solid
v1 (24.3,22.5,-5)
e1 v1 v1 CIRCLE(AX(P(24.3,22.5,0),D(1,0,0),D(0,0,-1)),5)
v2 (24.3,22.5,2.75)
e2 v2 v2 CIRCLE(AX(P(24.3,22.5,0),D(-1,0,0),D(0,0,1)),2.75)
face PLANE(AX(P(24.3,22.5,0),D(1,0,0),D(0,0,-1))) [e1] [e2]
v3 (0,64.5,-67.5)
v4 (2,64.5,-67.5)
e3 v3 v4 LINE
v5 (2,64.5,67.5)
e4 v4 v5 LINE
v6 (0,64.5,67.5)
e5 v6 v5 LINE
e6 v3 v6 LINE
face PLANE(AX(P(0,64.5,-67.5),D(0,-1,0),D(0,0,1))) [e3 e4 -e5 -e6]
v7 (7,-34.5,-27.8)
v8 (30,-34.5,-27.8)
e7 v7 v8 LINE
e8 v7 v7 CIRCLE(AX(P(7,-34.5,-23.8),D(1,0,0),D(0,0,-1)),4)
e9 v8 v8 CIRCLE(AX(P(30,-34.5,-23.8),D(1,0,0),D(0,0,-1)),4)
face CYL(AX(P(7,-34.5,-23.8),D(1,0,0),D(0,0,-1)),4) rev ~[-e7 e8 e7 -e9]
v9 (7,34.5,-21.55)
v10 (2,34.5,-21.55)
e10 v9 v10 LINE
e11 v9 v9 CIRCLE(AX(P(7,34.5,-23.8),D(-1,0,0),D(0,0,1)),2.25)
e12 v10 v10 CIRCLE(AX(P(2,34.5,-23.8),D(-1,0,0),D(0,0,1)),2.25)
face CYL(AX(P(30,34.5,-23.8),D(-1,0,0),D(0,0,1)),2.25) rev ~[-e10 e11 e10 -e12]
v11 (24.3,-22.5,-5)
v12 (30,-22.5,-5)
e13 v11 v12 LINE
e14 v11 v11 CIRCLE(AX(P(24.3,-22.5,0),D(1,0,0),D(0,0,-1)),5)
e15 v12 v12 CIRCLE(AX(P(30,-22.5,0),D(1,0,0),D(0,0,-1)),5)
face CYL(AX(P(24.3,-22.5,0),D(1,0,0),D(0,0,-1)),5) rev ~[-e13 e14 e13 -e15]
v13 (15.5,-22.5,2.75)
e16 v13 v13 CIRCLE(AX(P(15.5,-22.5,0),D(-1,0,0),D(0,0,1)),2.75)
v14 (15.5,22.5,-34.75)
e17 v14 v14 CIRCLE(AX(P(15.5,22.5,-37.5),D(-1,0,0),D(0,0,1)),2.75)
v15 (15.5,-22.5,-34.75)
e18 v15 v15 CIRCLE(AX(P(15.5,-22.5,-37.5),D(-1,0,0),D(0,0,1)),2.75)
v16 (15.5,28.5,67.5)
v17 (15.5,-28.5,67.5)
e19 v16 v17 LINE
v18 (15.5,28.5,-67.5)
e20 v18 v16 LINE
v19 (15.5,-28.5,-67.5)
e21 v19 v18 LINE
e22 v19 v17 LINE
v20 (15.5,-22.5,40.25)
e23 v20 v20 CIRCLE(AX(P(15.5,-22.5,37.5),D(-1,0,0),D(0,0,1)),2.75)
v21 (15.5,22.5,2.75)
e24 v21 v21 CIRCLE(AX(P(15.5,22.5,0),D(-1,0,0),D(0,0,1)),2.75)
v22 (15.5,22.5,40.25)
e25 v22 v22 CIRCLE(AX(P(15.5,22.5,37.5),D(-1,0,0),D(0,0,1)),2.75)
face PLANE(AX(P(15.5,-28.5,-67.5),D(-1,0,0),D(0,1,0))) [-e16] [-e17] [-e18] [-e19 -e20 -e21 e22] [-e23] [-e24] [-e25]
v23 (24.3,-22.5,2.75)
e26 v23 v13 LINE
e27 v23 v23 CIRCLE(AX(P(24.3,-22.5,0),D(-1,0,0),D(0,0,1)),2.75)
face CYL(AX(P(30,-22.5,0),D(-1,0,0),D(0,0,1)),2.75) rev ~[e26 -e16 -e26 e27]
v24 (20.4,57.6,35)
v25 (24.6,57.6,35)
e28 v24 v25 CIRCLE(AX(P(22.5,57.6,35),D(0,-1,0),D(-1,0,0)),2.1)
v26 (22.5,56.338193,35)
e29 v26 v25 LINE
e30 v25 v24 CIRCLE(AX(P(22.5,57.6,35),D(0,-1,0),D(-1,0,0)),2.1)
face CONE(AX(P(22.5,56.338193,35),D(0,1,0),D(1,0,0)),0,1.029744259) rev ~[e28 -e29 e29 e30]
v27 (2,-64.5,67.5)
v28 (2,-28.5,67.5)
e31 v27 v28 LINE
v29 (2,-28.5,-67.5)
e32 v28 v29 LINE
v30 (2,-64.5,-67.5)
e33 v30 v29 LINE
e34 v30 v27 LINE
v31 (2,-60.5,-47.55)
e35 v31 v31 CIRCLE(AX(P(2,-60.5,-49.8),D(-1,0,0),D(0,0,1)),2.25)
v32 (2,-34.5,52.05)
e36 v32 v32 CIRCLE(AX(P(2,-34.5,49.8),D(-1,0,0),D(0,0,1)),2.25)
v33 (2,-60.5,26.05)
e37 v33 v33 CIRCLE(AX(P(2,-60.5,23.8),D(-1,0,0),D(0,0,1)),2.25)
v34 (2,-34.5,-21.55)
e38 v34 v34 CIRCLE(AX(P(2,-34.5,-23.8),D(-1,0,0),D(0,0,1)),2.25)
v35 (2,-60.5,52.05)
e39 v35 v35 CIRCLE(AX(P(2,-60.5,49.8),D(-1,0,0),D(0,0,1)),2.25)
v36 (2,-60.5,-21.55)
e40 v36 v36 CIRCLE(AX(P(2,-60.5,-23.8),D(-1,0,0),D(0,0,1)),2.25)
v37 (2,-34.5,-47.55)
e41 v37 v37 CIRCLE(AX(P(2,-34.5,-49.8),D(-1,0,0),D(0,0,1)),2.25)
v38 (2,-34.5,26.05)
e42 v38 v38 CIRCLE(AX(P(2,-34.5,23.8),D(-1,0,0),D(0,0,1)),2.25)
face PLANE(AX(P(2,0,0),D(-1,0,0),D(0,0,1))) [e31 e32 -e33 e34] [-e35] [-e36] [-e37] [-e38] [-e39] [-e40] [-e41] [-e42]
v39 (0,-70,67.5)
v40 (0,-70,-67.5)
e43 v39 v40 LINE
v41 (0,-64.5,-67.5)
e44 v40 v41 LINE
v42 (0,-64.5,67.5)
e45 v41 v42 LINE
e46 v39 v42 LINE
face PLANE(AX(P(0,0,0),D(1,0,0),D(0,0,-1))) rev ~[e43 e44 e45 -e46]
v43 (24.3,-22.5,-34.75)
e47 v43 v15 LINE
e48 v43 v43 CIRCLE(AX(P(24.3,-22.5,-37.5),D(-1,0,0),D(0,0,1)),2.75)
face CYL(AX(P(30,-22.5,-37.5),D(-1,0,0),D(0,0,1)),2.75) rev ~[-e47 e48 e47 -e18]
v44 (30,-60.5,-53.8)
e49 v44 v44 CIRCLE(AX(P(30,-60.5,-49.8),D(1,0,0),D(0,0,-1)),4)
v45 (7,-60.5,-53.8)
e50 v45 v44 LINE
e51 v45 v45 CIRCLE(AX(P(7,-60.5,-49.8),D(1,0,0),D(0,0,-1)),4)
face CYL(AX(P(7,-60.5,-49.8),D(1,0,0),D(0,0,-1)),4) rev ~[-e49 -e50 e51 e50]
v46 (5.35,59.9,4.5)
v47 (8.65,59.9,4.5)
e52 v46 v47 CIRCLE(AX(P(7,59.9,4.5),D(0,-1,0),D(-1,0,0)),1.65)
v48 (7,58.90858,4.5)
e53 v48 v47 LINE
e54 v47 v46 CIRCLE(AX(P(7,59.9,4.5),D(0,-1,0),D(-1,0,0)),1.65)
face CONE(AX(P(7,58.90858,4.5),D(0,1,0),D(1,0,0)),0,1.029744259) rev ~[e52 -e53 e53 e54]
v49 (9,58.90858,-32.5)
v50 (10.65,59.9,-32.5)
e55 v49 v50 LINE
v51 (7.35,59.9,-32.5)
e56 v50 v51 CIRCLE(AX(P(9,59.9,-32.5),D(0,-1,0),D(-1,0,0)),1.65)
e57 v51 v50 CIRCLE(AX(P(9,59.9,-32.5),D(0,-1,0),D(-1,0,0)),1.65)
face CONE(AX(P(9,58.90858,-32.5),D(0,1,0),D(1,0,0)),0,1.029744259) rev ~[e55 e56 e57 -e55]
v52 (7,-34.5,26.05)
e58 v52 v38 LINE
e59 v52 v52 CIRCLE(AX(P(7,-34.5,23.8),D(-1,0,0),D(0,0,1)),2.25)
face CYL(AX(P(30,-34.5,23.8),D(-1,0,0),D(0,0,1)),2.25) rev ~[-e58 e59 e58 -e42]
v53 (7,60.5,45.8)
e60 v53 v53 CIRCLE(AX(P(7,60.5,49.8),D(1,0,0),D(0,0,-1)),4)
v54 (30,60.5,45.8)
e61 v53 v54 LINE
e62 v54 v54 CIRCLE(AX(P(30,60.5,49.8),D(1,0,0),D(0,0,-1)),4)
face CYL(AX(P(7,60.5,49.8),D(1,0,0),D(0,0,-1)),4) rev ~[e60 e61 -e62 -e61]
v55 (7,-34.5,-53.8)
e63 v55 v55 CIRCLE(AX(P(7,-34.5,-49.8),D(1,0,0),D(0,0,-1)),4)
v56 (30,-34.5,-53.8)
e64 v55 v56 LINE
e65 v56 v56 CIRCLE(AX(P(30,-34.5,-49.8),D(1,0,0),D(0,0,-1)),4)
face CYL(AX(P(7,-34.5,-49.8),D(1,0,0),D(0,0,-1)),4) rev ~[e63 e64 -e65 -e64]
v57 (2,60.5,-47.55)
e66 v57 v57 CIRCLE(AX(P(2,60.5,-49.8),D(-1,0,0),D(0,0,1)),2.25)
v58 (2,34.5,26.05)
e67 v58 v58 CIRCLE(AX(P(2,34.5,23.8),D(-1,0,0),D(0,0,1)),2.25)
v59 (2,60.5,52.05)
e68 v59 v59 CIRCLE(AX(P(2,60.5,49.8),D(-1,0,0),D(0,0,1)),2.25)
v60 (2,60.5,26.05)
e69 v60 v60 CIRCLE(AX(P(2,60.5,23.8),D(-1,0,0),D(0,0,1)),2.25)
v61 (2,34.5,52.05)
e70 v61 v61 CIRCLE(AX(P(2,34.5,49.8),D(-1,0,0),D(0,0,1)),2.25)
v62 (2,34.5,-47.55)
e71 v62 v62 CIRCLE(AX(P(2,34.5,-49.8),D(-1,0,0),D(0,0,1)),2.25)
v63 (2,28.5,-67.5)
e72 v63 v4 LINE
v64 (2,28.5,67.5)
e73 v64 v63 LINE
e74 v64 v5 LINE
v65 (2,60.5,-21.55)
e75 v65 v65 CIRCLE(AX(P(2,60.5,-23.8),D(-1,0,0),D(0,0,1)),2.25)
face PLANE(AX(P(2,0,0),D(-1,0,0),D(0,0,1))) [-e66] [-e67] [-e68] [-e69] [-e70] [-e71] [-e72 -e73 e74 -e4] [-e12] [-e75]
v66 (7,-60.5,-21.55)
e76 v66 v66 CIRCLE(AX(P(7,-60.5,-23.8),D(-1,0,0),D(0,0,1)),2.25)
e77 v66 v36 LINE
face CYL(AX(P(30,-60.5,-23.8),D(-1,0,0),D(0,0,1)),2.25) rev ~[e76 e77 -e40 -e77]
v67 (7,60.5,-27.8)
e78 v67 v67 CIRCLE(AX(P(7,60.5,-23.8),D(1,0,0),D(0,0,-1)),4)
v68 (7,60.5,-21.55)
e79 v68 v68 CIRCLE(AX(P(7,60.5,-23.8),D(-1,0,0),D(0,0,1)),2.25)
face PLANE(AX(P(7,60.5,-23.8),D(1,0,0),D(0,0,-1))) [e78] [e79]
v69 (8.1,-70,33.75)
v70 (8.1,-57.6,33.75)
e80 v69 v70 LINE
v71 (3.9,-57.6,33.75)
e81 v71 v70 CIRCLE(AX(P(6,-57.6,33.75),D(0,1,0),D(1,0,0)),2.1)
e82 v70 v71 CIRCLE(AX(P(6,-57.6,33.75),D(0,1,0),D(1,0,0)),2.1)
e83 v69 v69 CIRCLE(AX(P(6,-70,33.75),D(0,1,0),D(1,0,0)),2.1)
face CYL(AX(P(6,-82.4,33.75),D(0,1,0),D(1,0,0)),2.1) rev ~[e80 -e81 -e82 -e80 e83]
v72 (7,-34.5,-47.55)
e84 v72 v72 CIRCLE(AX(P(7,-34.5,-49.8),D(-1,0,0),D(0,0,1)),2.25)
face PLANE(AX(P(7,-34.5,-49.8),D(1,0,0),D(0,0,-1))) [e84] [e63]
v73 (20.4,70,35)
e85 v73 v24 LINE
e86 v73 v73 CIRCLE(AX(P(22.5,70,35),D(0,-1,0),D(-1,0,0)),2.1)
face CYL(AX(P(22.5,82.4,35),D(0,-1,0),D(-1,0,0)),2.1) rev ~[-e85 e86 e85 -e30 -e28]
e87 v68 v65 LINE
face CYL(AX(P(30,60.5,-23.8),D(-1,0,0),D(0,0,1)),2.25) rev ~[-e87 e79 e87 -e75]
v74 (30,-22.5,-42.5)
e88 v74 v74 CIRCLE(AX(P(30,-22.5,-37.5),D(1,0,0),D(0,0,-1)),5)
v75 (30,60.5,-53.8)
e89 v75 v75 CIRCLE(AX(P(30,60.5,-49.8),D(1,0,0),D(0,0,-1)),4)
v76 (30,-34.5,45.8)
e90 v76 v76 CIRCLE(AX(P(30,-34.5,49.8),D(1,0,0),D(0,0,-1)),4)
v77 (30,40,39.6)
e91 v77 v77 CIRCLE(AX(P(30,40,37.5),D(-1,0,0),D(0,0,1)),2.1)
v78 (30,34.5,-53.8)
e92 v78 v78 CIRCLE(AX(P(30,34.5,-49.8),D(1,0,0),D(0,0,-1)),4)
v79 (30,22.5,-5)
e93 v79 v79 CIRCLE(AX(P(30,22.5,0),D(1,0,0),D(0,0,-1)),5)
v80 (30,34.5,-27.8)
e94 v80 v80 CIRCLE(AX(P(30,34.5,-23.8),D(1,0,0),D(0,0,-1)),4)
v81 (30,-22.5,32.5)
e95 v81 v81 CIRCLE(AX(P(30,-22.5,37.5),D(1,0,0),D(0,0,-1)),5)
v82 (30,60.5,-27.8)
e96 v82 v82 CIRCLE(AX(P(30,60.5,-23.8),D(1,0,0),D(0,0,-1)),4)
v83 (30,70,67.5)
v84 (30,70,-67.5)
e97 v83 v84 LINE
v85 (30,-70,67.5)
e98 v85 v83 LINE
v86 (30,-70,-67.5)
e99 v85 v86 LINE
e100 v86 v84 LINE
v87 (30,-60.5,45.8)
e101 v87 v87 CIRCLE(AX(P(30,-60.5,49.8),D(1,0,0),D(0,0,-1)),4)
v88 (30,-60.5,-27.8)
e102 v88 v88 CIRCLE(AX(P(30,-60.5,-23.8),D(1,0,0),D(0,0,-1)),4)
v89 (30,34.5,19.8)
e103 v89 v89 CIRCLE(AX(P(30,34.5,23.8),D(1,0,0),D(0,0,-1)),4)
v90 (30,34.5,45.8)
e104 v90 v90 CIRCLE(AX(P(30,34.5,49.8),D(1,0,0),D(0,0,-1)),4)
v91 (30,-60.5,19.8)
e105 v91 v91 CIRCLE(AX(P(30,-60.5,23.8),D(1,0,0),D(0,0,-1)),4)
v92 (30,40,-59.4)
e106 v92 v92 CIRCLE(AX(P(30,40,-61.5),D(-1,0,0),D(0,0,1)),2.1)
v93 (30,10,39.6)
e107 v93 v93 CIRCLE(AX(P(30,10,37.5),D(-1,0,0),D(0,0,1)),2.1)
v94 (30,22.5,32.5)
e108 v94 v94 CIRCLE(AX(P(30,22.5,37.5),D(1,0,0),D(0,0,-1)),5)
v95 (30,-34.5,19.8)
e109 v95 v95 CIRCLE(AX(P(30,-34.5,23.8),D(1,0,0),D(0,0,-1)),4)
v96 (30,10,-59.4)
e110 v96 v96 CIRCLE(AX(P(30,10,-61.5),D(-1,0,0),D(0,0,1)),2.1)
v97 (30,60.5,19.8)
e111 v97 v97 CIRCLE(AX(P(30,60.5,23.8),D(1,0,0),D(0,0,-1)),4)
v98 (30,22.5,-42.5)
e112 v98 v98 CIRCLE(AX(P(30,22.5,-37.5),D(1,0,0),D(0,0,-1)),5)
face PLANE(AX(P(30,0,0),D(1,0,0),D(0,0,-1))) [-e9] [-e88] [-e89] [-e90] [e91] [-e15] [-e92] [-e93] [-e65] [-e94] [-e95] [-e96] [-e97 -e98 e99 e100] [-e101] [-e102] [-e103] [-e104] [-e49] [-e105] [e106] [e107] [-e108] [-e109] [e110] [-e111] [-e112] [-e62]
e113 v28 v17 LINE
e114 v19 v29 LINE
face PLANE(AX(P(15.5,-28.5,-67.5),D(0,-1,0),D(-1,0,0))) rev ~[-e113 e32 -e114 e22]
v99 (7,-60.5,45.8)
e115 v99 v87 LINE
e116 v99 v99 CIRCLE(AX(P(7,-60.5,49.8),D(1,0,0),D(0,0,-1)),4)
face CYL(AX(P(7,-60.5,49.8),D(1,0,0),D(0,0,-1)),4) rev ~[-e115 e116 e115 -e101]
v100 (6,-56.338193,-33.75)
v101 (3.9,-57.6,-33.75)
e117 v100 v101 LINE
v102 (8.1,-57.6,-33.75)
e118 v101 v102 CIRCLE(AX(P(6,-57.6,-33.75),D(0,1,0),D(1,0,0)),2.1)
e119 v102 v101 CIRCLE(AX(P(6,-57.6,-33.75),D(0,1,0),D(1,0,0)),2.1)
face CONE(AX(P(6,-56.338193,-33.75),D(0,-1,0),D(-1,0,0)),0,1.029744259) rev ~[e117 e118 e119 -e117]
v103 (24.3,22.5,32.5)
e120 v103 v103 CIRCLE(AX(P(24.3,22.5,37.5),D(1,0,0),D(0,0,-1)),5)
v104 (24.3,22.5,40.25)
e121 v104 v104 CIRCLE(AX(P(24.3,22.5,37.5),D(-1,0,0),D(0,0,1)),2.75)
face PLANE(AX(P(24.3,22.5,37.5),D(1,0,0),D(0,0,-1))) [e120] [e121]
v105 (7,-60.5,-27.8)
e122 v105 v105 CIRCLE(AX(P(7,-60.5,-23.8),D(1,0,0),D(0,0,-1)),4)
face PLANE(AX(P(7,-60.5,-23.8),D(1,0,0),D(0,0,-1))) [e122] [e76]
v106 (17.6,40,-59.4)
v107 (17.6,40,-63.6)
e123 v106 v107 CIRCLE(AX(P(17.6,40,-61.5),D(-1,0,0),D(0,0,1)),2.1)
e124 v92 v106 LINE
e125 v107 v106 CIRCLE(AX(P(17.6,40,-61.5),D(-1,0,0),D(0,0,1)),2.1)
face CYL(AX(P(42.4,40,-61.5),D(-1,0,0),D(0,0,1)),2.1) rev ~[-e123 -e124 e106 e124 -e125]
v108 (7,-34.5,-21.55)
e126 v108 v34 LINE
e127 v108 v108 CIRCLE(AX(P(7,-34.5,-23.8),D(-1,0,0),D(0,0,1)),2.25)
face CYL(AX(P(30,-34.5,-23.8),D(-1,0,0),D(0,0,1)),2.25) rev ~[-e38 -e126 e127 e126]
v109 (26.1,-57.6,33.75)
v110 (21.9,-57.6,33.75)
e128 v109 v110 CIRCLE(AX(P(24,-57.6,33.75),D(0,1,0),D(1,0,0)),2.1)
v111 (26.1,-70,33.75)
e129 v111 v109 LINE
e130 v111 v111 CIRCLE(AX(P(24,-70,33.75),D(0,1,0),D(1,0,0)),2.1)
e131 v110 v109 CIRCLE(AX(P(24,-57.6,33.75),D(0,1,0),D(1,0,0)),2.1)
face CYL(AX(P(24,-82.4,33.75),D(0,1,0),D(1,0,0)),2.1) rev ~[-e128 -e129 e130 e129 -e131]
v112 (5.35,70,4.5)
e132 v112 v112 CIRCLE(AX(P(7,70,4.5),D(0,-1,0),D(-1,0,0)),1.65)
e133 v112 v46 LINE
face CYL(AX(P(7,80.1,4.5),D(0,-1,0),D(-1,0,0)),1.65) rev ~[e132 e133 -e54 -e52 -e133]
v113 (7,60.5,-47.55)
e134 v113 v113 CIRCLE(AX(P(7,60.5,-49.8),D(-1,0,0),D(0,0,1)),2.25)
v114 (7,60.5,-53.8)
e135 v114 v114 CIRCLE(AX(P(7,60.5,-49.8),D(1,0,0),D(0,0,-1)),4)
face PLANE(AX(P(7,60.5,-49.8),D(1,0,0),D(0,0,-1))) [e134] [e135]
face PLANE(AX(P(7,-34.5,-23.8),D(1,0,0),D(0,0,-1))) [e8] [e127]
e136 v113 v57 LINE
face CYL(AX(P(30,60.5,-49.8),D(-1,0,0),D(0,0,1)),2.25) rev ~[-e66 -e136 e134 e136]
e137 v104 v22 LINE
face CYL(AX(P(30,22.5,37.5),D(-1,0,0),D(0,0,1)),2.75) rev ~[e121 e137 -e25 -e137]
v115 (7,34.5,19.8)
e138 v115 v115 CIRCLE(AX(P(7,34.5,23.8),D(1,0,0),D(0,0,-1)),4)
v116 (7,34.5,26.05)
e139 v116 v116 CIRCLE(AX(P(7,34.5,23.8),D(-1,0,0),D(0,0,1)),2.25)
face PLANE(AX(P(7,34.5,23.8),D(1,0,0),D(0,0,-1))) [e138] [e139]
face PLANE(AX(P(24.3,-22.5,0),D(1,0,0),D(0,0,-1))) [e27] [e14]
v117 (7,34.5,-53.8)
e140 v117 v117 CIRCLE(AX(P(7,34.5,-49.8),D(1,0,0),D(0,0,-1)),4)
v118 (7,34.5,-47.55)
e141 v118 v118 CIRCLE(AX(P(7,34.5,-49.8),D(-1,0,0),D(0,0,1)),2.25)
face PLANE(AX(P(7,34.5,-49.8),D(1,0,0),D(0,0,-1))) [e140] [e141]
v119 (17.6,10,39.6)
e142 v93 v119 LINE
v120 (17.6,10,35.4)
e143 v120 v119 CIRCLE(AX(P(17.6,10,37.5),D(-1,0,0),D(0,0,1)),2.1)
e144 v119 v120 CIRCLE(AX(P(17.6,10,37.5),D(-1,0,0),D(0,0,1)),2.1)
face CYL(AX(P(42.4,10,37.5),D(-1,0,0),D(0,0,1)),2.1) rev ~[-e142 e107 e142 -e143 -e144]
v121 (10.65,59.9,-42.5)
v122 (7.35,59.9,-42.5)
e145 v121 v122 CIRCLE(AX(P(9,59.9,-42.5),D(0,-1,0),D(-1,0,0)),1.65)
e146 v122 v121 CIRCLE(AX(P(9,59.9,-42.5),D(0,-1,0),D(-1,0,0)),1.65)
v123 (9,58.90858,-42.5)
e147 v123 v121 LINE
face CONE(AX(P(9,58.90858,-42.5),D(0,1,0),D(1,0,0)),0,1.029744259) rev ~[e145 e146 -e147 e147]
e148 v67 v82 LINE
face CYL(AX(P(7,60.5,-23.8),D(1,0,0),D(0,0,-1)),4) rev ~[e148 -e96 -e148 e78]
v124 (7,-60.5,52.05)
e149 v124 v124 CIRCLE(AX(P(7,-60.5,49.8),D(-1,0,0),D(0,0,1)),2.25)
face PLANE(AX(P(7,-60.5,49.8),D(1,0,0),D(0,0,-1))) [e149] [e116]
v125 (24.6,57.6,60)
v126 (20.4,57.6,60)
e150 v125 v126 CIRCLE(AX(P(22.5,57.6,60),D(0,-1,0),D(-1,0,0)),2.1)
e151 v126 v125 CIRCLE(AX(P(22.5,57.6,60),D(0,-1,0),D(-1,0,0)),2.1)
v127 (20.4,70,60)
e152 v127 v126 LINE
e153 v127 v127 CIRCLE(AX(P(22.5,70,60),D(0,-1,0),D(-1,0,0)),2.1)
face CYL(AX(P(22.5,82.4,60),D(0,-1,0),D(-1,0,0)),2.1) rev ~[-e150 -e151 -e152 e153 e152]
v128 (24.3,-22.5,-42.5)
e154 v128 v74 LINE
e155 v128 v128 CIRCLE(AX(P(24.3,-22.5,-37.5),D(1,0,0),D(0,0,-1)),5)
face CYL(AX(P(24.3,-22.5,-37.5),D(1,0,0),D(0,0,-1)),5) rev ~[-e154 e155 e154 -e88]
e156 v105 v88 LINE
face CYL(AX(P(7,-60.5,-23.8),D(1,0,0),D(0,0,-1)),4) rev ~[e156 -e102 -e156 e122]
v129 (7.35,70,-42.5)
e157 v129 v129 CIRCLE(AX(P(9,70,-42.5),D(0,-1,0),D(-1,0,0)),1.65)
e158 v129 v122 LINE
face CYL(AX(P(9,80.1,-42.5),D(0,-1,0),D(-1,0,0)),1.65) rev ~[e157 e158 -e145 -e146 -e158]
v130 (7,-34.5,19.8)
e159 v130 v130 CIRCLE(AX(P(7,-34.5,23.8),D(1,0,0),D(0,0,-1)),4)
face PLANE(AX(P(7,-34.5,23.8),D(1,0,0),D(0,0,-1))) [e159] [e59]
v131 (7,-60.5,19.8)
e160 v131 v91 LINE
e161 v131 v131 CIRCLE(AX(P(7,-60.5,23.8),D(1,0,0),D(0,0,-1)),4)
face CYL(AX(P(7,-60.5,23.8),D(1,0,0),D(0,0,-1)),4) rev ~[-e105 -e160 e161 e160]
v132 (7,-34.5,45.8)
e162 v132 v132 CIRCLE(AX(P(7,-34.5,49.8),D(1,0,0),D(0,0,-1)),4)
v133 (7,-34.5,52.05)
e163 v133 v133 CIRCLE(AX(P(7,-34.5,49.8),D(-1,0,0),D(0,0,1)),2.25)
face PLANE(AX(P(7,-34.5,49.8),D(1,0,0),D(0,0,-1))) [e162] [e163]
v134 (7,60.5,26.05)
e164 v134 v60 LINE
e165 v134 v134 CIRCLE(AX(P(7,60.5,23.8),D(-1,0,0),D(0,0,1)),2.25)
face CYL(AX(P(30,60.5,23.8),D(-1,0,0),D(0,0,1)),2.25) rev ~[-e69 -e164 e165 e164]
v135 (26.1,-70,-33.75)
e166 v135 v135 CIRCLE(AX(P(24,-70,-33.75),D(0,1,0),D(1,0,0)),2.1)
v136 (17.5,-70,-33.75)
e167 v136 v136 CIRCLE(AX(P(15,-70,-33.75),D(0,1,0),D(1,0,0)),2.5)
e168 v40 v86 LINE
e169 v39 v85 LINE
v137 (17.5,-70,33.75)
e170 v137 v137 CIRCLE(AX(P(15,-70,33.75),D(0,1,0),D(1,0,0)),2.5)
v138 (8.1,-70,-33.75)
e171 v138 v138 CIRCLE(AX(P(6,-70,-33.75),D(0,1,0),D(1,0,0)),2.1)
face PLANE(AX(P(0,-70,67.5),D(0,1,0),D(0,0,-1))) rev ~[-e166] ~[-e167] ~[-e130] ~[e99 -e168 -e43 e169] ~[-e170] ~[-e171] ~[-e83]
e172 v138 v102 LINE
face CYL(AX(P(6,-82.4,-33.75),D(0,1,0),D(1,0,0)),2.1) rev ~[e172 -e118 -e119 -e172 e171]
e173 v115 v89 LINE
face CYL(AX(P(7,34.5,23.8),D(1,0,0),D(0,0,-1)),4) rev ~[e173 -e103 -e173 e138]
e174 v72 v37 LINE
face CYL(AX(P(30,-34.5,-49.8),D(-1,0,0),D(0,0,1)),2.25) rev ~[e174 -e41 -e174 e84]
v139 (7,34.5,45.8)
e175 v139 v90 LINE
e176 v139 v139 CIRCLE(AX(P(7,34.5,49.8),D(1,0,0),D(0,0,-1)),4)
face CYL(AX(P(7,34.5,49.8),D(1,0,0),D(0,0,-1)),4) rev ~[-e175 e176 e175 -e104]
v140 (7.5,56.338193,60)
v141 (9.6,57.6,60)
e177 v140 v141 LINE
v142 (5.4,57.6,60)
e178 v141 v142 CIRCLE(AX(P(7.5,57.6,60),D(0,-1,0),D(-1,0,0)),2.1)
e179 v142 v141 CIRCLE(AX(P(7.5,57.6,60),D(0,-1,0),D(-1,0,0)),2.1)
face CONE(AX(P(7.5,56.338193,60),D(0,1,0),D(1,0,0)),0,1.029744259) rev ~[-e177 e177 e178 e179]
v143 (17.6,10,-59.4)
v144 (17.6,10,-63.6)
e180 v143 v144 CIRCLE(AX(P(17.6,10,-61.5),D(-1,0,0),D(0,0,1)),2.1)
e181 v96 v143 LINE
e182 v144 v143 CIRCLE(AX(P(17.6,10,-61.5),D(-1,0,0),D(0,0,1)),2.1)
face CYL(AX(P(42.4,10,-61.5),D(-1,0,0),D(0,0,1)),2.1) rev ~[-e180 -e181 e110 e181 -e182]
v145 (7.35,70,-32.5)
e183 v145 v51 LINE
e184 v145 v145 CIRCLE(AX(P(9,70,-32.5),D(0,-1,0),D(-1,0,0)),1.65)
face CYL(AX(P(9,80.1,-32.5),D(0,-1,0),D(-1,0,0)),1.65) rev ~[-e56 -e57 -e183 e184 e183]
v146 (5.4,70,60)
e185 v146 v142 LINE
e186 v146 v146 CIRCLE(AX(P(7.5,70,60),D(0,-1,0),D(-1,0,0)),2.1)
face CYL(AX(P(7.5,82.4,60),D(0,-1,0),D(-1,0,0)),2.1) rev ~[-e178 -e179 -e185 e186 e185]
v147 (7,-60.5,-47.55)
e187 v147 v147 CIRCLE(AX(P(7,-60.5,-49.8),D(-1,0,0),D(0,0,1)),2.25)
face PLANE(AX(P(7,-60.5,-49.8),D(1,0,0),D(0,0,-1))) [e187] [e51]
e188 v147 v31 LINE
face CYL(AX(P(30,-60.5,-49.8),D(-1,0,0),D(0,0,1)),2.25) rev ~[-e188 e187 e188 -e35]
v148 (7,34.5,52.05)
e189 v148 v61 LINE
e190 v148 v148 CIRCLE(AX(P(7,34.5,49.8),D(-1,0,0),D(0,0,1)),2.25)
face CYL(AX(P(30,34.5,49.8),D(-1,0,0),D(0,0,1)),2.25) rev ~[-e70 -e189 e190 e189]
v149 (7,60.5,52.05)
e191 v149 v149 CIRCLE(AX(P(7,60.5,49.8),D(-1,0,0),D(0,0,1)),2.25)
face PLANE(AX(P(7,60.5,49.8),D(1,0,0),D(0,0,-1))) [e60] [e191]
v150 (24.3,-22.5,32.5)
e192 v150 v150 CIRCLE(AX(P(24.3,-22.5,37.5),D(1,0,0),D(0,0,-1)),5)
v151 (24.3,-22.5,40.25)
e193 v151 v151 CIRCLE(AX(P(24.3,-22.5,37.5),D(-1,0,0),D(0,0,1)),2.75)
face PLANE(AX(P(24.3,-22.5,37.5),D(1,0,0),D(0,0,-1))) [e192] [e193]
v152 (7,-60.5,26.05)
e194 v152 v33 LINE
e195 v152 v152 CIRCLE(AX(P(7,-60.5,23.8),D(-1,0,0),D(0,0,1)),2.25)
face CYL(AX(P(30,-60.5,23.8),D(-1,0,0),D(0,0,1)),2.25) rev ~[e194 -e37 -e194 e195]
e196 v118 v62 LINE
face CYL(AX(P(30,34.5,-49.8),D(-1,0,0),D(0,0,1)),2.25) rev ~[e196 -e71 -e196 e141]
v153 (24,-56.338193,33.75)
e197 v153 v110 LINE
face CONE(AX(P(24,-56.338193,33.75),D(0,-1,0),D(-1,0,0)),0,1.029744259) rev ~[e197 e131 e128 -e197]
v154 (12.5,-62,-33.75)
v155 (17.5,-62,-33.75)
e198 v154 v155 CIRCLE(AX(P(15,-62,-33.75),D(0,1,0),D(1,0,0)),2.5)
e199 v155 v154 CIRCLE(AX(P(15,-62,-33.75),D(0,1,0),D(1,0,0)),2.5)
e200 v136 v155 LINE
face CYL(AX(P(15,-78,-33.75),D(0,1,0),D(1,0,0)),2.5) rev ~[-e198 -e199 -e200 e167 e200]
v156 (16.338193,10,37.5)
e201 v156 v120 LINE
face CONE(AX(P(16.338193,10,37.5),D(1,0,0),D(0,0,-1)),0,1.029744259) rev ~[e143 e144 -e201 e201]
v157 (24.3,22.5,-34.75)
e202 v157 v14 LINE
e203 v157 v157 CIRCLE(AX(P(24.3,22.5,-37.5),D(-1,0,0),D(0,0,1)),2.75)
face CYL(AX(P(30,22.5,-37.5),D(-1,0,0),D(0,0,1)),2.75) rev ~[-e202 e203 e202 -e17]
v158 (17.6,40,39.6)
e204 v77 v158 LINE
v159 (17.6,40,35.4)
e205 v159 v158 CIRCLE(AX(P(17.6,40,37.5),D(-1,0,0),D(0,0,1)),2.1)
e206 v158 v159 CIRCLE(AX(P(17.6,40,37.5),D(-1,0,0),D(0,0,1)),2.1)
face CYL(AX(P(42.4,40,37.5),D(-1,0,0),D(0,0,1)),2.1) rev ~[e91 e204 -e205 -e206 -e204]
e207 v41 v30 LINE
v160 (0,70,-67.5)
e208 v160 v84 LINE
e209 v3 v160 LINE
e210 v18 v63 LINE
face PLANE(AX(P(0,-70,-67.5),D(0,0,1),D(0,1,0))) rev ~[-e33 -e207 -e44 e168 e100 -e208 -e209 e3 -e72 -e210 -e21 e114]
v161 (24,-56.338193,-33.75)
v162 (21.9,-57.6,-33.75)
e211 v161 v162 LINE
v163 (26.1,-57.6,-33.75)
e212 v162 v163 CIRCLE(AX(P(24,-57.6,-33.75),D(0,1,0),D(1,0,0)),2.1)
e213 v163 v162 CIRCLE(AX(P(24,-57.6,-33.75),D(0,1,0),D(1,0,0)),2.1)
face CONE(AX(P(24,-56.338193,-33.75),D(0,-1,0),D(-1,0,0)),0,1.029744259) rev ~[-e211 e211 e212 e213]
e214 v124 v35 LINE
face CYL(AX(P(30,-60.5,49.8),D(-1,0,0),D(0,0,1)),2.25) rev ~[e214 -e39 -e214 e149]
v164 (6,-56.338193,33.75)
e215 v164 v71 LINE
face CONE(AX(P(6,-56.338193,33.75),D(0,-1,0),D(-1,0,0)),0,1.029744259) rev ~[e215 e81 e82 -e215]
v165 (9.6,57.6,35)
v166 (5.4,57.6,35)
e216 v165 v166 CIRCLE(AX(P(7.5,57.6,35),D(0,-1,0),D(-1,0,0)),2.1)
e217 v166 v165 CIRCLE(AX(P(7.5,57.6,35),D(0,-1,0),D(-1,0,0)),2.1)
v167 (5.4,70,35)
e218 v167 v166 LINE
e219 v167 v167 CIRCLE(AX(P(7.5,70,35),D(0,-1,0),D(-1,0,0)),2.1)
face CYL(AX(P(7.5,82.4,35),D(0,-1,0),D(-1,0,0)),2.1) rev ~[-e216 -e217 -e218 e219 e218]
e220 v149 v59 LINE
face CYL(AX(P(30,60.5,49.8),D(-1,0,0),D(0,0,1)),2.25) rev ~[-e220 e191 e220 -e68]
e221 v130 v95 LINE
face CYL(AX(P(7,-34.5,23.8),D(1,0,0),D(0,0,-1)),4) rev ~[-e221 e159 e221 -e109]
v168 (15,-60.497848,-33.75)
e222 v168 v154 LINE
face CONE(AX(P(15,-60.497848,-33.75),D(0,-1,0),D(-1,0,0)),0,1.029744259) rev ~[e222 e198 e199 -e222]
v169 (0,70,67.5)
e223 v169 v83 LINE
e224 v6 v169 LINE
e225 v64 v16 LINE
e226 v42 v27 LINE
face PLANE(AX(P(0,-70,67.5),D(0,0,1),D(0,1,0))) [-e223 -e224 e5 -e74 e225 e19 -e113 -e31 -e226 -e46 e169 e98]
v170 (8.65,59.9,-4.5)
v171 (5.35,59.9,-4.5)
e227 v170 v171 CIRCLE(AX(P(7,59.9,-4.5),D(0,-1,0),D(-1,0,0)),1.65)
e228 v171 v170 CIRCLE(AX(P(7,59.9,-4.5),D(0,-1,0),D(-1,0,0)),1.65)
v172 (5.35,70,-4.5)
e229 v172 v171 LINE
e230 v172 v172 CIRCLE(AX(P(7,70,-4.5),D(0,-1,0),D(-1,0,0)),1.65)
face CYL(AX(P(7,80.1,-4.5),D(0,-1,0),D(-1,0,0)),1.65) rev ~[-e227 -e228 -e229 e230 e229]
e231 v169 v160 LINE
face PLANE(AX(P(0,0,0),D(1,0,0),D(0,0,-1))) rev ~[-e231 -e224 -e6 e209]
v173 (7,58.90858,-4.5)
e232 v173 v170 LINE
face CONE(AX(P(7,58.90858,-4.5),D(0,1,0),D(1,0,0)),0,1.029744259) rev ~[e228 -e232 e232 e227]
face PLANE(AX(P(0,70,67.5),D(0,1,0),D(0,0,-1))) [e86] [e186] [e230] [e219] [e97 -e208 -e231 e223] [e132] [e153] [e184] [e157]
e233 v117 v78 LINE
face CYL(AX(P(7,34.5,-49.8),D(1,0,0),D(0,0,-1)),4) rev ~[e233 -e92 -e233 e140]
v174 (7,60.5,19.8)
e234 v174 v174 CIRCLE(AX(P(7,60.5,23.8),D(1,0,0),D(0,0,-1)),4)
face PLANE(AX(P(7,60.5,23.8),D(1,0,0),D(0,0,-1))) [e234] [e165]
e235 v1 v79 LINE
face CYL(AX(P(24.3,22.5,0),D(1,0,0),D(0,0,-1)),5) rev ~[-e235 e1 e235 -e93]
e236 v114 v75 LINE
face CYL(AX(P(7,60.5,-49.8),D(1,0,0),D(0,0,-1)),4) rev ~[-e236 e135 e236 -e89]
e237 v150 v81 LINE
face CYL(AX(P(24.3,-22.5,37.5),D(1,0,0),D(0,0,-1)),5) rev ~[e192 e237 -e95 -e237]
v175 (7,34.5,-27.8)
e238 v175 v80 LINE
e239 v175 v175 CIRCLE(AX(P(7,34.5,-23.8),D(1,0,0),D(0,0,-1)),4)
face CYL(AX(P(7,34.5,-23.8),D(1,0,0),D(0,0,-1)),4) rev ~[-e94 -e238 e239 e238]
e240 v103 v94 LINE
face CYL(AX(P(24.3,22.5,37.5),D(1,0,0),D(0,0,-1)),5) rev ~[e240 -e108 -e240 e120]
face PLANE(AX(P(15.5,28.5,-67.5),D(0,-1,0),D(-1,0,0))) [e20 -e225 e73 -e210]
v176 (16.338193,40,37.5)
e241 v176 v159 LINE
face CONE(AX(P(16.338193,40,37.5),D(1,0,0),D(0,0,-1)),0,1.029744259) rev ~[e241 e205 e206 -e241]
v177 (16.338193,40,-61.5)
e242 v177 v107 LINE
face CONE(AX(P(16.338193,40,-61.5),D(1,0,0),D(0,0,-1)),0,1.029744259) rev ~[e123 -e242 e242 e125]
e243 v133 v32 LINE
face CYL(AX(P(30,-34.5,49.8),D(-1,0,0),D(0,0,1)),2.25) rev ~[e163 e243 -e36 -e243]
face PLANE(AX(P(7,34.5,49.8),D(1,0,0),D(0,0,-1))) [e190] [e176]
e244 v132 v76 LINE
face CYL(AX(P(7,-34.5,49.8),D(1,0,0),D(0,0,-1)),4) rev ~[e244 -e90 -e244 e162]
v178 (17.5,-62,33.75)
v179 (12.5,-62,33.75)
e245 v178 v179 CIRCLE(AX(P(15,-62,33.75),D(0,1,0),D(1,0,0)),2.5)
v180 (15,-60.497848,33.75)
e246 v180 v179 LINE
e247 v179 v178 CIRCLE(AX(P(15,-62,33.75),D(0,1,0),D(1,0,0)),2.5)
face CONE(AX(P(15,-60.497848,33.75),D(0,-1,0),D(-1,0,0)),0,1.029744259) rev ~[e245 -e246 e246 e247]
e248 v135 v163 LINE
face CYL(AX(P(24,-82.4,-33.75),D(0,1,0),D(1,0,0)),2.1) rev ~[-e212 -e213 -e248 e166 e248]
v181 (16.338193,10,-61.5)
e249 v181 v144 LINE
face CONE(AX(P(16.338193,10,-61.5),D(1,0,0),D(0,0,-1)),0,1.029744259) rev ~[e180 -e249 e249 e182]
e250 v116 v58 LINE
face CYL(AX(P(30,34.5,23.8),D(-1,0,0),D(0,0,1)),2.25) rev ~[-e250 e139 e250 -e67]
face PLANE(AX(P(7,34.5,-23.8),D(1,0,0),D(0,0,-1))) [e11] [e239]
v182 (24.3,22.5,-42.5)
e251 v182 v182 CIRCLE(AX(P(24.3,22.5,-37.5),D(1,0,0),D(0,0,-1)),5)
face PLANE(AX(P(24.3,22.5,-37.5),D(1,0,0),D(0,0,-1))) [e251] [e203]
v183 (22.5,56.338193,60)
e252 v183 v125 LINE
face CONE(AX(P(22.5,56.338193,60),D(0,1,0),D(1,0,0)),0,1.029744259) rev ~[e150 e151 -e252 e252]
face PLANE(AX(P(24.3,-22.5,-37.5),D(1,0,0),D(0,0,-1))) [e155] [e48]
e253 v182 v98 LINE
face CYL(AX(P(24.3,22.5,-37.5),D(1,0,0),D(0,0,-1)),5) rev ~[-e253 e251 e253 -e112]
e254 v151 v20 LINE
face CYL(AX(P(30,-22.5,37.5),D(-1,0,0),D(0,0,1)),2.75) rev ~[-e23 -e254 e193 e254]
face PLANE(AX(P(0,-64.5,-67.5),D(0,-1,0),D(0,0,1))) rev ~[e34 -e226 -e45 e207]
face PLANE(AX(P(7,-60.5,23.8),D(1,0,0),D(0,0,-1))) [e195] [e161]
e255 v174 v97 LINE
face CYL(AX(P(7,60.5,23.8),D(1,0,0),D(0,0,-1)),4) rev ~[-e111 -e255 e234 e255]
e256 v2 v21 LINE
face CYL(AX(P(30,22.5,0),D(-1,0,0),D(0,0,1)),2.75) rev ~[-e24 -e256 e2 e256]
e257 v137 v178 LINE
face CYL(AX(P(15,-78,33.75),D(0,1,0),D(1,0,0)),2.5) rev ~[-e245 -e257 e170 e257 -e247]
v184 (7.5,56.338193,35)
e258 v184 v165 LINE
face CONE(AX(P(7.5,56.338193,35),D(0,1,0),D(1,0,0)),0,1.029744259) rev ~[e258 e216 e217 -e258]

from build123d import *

# Parameters (mm, degrees)
SKETCH1_W                                            = 135
SKETCH1_H                                            = 140
BOSS_EXTRUDE1_DEPTH                                  = 30
SKETCH2_W                                            = 15.5
SKETCH2_H                                            = 57
CUT_EXTRUDE1_DEPTH                                   = 156
SKETCH3_W                                            = 135
SKETCH3_H                                            = 129
CUT_EXTRUDE2_DEPTH                                   = 2
M4_TAPPED_HOLE1_D                                    = 3.3
M4_TAPPED_HOLE1_DEPTH                                = 10.1
M4_TAPPED_HOLE1_TIP                                  = 0.991420021
M5_TAPPED_HOLE1_D                                    = 4.2
M5_TAPPED_HOLE1_DEPTH                                = 12.4
M5_TAPPED_HOLE1_TIP                                  = 1.2618073
F_5_0MM_DOWEL_HOLE1_D                                = 5
F_5_0MM_DOWEL_HOLE1_DEPTH                            = 8
F_5_0MM_DOWEL_HOLE1_TIP                              = 1.502151548
M5_TAPPED_HOLE2_D                                    = 4.2
M5_TAPPED_HOLE2_DEPTH                                = 12.4
M5_TAPPED_HOLE2_TIP                                  = 1.2618073
CBORE_FOR_M4_HEXAGON_SOCKET_HEAD_CAP_SCR_D           = 4.5
CBORE_FOR_M4_HEXAGON_SOCKET_HEAD_CAP_SCR_CBORE_D     = 8
CBORE_FOR_M4_HEXAGON_SOCKET_HEAD_CAP_SCR_CBORE_DEPTH = 23
CBORE_FOR_M5_HEXAGON_SOCKET_HEAD_CAP_SCR_D           = 5.5
CBORE_FOR_M5_HEXAGON_SOCKET_HEAD_CAP_SCR_CBORE_D     = 10
CBORE_FOR_M5_HEXAGON_SOCKET_HEAD_CAP_SCR_CBORE_DEPTH = 5.7
LPATTERN1_COUNT                                      = 2
LPATTERN1_PITCH                                      = 37.5
LPATTERN1_COL_COUNT                                  = 2
LPATTERN1_COL_PITCH                                  = 37.5
M5_TAPPED_HOLE3_D                                    = 4.2
M5_TAPPED_HOLE3_DEPTH                                = 12.4
M5_TAPPED_HOLE3_TIP                                  = 1.2618073
M4_TAPPED_HOLE2_D                                    = 3.3
M4_TAPPED_HOLE2_DEPTH                                = 10.1
M4_TAPPED_HOLE2_TIP                                  = 0.991420021


with BuildPart() as part:
    # Sketch1 → Boss-Extrude1 (new body)
    with BuildSketch(Plane(origin=(0, 0, 0), x_dir=(0, 0, -1), z_dir=(1, 0, 0))):
        Rectangle(SKETCH1_W, SKETCH1_H)
    extrude(amount=BOSS_EXTRUDE1_DEPTH)

    # Sketch2 → Cut-Extrude1 (cut, through all)
    with BuildSketch(Plane(origin=(0, 0, -67.5), x_dir=(-1, 0, 0), z_dir=(0, 0, -1))):
        with Locations((-7.75, 0)):
            Rectangle(SKETCH2_W, SKETCH2_H)
    extrude(amount=-CUT_EXTRUDE1_DEPTH, mode=Mode.SUBTRACT)

    # Sketch3 → Cut-Extrude2 (cut)
    with BuildSketch(Plane.ZY):
        Rectangle(SKETCH3_W, SKETCH3_H)
    extrude(amount=-CUT_EXTRUDE2_DEPTH, mode=Mode.SUBTRACT)

    # M4 Tapped Hole1
    with Locations(Plane(origin=(0, 70, 0), x_dir=(1, 0, 0), z_dir=(0, 1, 0))):
        with Locations((7, 4.5), (7, -4.5)):
            Hole(M4_TAPPED_HOLE1_D / 2, depth=M4_TAPPED_HOLE1_DEPTH)
            with Locations((0, 0, -(M4_TAPPED_HOLE1_DEPTH + M4_TAPPED_HOLE1_TIP / 2))):  # 118° drill point
                Cone(0, M4_TAPPED_HOLE1_D / 2, M4_TAPPED_HOLE1_TIP, mode=Mode.SUBTRACT)

    # M5 Tapped Hole1
    with Locations(Plane(origin=(0, -70, 0), x_dir=(-1, 0, 0), z_dir=(0, -1, 0))):
        with Locations((-24, 33.75), (-6, 33.75), (-24, -33.75), (-6, -33.75)):
            Hole(M5_TAPPED_HOLE1_D / 2, depth=M5_TAPPED_HOLE1_DEPTH)
            with Locations((0, 0, -(M5_TAPPED_HOLE1_DEPTH + M5_TAPPED_HOLE1_TIP / 2))):  # 118° drill point
                Cone(0, M5_TAPPED_HOLE1_D / 2, M5_TAPPED_HOLE1_TIP, mode=Mode.SUBTRACT)

    # Ø5.0mm dowel hole1
    with Locations(Plane(origin=(0, -70, 0), x_dir=(-1, 0, 0), z_dir=(0, -1, 0))):
        with Locations((-15, 33.75), (-15, -33.75)):
            Hole(F_5_0MM_DOWEL_HOLE1_D / 2, depth=F_5_0MM_DOWEL_HOLE1_DEPTH)
            with Locations((0, 0, -(F_5_0MM_DOWEL_HOLE1_DEPTH + F_5_0MM_DOWEL_HOLE1_TIP / 2))):  # 118° drill point
                Cone(0, F_5_0MM_DOWEL_HOLE1_D / 2, F_5_0MM_DOWEL_HOLE1_TIP, mode=Mode.SUBTRACT)

    # M5 Tapped Hole2
    with Locations(Plane(origin=(30, 0, 0), x_dir=(0, 0, -1), z_dir=(1, 0, 0))):
        with Locations((-37.5, 40), (-37.5, 10), (61.5, 40), (61.5, 10)):
            Hole(M5_TAPPED_HOLE2_D / 2, depth=M5_TAPPED_HOLE2_DEPTH)
            with Locations((0, 0, -(M5_TAPPED_HOLE2_DEPTH + M5_TAPPED_HOLE2_TIP / 2))):  # 118° drill point
                Cone(0, M5_TAPPED_HOLE2_D / 2, M5_TAPPED_HOLE2_TIP, mode=Mode.SUBTRACT)

    # CBORE for M4 Hexagon socket head cap screws1 (through all)
    with Locations(Plane(origin=(30, 0, 0), x_dir=(0, 0, -1), z_dir=(1, 0, 0))):
        with Locations((-49.8, 60.5), (-23.8, 60.5), (-23.8, 34.5), (-49.8, 34.5), (49.8, 34.5), (23.8, 34.5), (23.8, 60.5), (49.8, 60.5), (49.8, -60.5), (23.8, -60.5), (23.8, -34.5), (49.8, -34.5), (-49.8, -34.5), (-23.8, -34.5), (-23.8, -60.5), (-49.8, -60.5)):
            CounterBoreHole(CBORE_FOR_M4_HEXAGON_SOCKET_HEAD_CAP_SCR_D / 2, CBORE_FOR_M4_HEXAGON_SOCKET_HEAD_CAP_SCR_CBORE_D / 2, CBORE_FOR_M4_HEXAGON_SOCKET_HEAD_CAP_SCR_CBORE_DEPTH)

    # CBORE for M5 Hexagon socket head cap screws1 (through all)
    with Locations(Plane(origin=(30, 0, 0), x_dir=(0, 0, -1), z_dir=(1, 0, 0))):
        with Locations((0, 22.5), (0, -22.5)):
            cbore_for_m5_hexagon_socket_head_cap_scr = CounterBoreHole(CBORE_FOR_M5_HEXAGON_SOCKET_HEAD_CAP_SCR_D / 2, CBORE_FOR_M5_HEXAGON_SOCKET_HEAD_CAP_SCR_CBORE_D / 2, CBORE_FOR_M5_HEXAGON_SOCKET_HEAD_CAP_SCR_CBORE_DEPTH)

    # LPattern1: CBORE for M5 Hexagon socket head cap screws1 ×2
    with Locations(*[(0, 0, i * LPATTERN1_PITCH) for i in range(1, LPATTERN1_COUNT)]):
        add(cbore_for_m5_hexagon_socket_head_cap_scr, mode=Mode.SUBTRACT)

    # LPattern1 col: CBORE for M5 Hexagon socket head cap screws1 ×2
    with Locations(*[(0, 0, -i * LPATTERN1_COL_PITCH) for i in range(1, LPATTERN1_COL_COUNT)]):
        add(cbore_for_m5_hexagon_socket_head_cap_scr, mode=Mode.SUBTRACT)

    # M5 Tapped Hole3
    with Locations(Plane(origin=(0, 70, 0), x_dir=(1, 0, 0), z_dir=(0, 1, 0))):
        with Locations((7.5, -60), (22.5, -60), (22.5, -35), (7.5, -35)):
            Hole(M5_TAPPED_HOLE3_D / 2, depth=M5_TAPPED_HOLE3_DEPTH)
            with Locations((0, 0, -(M5_TAPPED_HOLE3_DEPTH + M5_TAPPED_HOLE3_TIP / 2))):  # 118° drill point
                Cone(0, M5_TAPPED_HOLE3_D / 2, M5_TAPPED_HOLE3_TIP, mode=Mode.SUBTRACT)

    # M4 Tapped Hole2
    with Locations(Plane(origin=(0, 70, 0), x_dir=(1, 0, 0), z_dir=(0, 1, 0))):
        with Locations((9, 42.5), (9, 32.5)):
            Hole(M4_TAPPED_HOLE2_D / 2, depth=M4_TAPPED_HOLE2_DEPTH)
            with Locations((0, 0, -(M4_TAPPED_HOLE2_DEPTH + M4_TAPPED_HOLE2_TIP / 2))):  # 118° drill point
                Cone(0, M4_TAPPED_HOLE2_D / 2, M4_TAPPED_HOLE2_TIP, mode=Mode.SUBTRACT)


solid = part.part
